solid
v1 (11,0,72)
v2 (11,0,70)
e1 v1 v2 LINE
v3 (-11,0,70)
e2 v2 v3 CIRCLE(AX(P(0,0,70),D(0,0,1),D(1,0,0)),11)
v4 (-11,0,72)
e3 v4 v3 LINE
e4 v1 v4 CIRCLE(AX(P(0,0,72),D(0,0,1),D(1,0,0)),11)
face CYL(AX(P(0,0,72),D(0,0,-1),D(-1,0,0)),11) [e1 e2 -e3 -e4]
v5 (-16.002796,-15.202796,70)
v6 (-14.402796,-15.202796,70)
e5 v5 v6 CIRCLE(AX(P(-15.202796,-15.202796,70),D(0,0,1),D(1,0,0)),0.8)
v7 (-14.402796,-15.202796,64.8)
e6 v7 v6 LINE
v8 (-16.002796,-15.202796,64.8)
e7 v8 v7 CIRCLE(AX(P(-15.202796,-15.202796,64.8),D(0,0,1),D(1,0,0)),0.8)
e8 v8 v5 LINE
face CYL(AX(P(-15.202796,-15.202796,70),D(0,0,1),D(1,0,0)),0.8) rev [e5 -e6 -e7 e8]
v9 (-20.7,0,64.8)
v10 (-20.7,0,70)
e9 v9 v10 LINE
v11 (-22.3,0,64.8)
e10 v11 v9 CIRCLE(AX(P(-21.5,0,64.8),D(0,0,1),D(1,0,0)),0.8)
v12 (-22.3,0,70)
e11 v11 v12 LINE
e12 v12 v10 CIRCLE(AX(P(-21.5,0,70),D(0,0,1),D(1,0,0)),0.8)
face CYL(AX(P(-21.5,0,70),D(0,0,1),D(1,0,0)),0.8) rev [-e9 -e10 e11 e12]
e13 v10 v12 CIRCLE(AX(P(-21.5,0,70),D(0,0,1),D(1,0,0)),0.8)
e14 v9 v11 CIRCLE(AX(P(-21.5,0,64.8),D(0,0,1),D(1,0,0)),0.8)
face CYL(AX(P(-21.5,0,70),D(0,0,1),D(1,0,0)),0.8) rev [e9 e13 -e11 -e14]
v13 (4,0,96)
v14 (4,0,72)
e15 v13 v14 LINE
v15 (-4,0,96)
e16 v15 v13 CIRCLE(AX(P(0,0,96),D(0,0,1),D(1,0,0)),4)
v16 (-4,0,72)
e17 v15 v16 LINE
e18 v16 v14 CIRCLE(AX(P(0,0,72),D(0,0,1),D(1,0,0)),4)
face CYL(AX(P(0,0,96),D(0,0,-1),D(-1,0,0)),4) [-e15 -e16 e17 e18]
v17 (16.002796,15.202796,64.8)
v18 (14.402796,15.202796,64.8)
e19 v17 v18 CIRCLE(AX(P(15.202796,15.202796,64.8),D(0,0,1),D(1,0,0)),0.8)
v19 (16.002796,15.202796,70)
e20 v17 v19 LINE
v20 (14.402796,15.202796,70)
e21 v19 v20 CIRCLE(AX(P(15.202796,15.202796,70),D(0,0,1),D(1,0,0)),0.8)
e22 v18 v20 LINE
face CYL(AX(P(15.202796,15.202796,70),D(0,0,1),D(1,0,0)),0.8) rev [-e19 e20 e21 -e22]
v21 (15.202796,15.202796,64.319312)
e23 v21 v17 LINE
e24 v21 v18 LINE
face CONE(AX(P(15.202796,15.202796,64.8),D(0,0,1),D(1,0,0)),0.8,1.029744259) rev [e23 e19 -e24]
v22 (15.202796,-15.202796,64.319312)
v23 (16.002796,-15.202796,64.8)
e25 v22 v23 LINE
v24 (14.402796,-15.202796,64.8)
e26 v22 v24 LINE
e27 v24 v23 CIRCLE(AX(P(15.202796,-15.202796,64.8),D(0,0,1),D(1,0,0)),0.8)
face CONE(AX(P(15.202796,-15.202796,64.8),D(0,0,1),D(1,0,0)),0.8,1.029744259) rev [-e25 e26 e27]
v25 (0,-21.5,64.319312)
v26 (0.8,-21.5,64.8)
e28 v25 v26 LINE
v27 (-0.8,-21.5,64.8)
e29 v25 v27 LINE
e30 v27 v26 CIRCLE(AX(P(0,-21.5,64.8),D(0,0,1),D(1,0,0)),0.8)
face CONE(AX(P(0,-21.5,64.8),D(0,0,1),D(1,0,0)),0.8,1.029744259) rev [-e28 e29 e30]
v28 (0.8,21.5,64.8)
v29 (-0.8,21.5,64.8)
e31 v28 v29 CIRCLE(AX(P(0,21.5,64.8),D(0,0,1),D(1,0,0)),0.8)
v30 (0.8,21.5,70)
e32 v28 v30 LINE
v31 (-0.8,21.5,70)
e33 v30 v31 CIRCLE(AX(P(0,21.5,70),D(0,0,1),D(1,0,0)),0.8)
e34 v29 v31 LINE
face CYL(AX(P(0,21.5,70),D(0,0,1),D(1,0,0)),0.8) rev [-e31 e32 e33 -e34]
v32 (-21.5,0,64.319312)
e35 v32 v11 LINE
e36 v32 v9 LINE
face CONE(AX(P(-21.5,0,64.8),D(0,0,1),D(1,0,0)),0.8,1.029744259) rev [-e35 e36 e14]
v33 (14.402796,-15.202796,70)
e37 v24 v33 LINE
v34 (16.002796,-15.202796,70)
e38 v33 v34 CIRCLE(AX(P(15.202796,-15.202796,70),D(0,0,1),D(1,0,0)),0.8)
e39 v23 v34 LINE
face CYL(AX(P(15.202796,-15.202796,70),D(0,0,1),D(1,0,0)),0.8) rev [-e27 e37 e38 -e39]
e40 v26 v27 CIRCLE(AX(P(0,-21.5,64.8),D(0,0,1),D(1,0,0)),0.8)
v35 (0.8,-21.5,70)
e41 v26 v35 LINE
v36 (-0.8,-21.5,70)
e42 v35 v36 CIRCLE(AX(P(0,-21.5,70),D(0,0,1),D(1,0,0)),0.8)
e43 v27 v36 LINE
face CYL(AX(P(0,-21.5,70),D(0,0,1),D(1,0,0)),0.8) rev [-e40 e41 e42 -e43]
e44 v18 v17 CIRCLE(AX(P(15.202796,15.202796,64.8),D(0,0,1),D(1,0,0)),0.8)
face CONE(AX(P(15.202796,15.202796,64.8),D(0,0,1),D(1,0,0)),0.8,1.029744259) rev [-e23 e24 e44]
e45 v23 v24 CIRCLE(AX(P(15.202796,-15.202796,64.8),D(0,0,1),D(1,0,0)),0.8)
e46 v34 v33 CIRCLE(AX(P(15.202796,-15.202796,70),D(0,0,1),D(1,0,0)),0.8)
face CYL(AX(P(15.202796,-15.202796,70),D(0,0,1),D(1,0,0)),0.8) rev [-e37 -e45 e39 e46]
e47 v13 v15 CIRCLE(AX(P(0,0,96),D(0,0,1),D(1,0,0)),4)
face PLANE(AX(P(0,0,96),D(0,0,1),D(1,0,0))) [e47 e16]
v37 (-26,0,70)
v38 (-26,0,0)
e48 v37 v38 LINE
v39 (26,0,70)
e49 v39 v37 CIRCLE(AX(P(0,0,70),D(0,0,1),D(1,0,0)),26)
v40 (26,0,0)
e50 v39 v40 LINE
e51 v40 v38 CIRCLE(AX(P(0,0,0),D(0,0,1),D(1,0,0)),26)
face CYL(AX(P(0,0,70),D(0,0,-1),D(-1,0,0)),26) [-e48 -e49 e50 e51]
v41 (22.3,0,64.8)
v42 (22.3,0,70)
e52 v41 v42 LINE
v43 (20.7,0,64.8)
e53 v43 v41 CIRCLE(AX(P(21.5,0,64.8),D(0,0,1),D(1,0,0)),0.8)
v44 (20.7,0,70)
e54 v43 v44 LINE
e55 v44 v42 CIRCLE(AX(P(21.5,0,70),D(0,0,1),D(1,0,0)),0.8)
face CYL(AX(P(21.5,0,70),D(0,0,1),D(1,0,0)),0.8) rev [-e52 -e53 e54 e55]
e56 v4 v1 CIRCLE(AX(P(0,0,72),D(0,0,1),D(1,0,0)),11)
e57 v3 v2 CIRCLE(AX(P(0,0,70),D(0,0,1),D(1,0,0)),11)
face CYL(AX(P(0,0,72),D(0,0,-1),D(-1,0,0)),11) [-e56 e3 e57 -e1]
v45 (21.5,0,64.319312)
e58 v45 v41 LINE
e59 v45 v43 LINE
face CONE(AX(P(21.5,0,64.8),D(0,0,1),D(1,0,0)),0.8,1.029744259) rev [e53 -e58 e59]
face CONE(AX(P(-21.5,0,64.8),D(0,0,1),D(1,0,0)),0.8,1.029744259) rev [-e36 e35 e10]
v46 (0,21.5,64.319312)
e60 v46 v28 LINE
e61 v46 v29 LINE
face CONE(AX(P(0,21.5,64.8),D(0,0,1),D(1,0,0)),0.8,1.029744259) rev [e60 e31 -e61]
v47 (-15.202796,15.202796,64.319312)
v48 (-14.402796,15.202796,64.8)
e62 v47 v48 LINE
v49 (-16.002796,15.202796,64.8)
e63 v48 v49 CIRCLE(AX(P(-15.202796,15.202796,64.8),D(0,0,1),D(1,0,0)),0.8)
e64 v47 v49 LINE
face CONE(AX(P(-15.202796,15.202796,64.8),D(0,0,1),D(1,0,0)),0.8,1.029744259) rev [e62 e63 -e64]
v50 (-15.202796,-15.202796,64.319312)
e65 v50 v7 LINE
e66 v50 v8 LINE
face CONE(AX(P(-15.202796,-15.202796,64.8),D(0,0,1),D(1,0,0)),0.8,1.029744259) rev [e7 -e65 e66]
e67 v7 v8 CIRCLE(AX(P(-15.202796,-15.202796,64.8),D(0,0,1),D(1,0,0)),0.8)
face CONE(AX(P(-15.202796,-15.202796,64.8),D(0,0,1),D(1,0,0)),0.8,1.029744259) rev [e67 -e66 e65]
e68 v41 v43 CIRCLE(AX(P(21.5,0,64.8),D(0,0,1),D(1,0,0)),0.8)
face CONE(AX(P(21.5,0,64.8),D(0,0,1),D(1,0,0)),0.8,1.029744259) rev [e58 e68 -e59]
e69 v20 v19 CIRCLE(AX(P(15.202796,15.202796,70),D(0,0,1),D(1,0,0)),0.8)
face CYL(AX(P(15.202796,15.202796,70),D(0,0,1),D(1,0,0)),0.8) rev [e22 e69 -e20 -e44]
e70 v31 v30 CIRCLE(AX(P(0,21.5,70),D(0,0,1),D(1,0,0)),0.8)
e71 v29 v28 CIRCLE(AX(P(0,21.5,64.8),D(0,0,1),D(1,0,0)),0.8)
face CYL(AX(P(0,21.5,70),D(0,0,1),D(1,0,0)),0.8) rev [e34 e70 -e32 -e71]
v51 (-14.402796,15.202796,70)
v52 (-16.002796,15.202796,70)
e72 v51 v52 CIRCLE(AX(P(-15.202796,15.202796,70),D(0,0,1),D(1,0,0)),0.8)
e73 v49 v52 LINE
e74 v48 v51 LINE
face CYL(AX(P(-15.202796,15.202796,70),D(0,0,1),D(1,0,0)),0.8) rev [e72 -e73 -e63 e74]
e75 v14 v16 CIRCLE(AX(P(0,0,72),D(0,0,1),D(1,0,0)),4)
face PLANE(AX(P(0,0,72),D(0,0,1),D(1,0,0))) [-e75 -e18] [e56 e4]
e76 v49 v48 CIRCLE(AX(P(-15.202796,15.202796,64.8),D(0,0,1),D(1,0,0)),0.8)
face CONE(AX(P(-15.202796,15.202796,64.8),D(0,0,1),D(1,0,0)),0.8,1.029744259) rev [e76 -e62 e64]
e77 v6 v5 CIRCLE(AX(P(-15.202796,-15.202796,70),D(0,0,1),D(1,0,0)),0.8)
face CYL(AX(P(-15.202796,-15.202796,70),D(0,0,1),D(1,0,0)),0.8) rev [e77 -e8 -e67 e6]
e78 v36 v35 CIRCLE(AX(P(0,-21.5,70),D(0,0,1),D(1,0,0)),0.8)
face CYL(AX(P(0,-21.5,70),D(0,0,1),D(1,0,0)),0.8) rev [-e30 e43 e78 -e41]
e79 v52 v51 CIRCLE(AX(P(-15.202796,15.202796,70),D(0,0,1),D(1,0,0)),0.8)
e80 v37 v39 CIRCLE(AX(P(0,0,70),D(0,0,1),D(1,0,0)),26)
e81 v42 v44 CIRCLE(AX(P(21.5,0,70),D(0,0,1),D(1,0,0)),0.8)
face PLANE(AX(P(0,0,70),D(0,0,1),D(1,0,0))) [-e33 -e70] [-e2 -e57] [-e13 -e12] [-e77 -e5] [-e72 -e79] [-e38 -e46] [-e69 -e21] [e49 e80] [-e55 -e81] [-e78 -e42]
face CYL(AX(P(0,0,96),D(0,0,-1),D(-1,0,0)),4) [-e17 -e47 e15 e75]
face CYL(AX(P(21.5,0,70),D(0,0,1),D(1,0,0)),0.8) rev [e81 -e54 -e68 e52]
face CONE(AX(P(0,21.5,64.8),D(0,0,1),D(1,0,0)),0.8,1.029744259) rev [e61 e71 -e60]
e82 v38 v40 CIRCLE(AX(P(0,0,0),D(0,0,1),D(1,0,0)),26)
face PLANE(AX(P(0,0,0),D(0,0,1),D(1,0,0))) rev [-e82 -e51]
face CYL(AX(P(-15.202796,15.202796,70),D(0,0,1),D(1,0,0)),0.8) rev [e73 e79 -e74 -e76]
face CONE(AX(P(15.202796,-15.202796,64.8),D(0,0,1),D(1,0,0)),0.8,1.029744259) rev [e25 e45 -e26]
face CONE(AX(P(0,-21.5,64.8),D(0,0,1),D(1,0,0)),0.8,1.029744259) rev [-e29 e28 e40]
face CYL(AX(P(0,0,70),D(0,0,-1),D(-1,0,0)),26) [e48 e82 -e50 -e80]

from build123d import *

# Parameters (mm, degrees)
SKETCH_1_R             = 26
EXTRUDE_1_DEPTH        = 70
SKETCH_2_R             = 11
EXTRUDE_2_DEPTH        = 2
SKETCH_3_R             = 4
EXTRUDE_3_DEPTH        = 24
HOLE_WIZARD_M2_1_D     = 1.6
HOLE_WIZARD_M2_1_DEPTH = 5.2
HOLE_WIZARD_M2_1_TIP   = 0.480688495


with BuildPart() as part:
    # 草图1 → 凸台-拉伸1 (new body)
    with BuildSketch(Plane.XY):
        Circle(SKETCH_1_R)
    extrude(amount=EXTRUDE_1_DEPTH)

    # 草图2 → 凸台-拉伸2 (add)
    with BuildSketch(Plane.XY.offset(70)):
        Circle(SKETCH_2_R)
    extrude(amount=EXTRUDE_2_DEPTH)

    # 草图3 → 凸台-拉伸3 (add)
    with BuildSketch(Plane.XY.offset(72)):
        Circle(SKETCH_3_R)
    extrude(amount=EXTRUDE_3_DEPTH)

    # M2 螺纹孔1
    with Locations(Plane.XY.offset(70)):
        with Locations((0, 21.5), (15.202795796, 15.202795796), (21.5, 0), (15.202795796, -15.202795796), (0, -21.5), (-15.202795796, -15.202795796), (-21.5, 0), (-15.202795796, 15.202795796)):
            Hole(HOLE_WIZARD_M2_1_D / 2, depth=HOLE_WIZARD_M2_1_DEPTH)
            with Locations((0, 0, -(HOLE_WIZARD_M2_1_DEPTH + HOLE_WIZARD_M2_1_TIP / 2))):  # 118° drill point
                Cone(0, HOLE_WIZARD_M2_1_D / 2, HOLE_WIZARD_M2_1_TIP, mode=Mode.SUBTRACT)


solid = part.part
